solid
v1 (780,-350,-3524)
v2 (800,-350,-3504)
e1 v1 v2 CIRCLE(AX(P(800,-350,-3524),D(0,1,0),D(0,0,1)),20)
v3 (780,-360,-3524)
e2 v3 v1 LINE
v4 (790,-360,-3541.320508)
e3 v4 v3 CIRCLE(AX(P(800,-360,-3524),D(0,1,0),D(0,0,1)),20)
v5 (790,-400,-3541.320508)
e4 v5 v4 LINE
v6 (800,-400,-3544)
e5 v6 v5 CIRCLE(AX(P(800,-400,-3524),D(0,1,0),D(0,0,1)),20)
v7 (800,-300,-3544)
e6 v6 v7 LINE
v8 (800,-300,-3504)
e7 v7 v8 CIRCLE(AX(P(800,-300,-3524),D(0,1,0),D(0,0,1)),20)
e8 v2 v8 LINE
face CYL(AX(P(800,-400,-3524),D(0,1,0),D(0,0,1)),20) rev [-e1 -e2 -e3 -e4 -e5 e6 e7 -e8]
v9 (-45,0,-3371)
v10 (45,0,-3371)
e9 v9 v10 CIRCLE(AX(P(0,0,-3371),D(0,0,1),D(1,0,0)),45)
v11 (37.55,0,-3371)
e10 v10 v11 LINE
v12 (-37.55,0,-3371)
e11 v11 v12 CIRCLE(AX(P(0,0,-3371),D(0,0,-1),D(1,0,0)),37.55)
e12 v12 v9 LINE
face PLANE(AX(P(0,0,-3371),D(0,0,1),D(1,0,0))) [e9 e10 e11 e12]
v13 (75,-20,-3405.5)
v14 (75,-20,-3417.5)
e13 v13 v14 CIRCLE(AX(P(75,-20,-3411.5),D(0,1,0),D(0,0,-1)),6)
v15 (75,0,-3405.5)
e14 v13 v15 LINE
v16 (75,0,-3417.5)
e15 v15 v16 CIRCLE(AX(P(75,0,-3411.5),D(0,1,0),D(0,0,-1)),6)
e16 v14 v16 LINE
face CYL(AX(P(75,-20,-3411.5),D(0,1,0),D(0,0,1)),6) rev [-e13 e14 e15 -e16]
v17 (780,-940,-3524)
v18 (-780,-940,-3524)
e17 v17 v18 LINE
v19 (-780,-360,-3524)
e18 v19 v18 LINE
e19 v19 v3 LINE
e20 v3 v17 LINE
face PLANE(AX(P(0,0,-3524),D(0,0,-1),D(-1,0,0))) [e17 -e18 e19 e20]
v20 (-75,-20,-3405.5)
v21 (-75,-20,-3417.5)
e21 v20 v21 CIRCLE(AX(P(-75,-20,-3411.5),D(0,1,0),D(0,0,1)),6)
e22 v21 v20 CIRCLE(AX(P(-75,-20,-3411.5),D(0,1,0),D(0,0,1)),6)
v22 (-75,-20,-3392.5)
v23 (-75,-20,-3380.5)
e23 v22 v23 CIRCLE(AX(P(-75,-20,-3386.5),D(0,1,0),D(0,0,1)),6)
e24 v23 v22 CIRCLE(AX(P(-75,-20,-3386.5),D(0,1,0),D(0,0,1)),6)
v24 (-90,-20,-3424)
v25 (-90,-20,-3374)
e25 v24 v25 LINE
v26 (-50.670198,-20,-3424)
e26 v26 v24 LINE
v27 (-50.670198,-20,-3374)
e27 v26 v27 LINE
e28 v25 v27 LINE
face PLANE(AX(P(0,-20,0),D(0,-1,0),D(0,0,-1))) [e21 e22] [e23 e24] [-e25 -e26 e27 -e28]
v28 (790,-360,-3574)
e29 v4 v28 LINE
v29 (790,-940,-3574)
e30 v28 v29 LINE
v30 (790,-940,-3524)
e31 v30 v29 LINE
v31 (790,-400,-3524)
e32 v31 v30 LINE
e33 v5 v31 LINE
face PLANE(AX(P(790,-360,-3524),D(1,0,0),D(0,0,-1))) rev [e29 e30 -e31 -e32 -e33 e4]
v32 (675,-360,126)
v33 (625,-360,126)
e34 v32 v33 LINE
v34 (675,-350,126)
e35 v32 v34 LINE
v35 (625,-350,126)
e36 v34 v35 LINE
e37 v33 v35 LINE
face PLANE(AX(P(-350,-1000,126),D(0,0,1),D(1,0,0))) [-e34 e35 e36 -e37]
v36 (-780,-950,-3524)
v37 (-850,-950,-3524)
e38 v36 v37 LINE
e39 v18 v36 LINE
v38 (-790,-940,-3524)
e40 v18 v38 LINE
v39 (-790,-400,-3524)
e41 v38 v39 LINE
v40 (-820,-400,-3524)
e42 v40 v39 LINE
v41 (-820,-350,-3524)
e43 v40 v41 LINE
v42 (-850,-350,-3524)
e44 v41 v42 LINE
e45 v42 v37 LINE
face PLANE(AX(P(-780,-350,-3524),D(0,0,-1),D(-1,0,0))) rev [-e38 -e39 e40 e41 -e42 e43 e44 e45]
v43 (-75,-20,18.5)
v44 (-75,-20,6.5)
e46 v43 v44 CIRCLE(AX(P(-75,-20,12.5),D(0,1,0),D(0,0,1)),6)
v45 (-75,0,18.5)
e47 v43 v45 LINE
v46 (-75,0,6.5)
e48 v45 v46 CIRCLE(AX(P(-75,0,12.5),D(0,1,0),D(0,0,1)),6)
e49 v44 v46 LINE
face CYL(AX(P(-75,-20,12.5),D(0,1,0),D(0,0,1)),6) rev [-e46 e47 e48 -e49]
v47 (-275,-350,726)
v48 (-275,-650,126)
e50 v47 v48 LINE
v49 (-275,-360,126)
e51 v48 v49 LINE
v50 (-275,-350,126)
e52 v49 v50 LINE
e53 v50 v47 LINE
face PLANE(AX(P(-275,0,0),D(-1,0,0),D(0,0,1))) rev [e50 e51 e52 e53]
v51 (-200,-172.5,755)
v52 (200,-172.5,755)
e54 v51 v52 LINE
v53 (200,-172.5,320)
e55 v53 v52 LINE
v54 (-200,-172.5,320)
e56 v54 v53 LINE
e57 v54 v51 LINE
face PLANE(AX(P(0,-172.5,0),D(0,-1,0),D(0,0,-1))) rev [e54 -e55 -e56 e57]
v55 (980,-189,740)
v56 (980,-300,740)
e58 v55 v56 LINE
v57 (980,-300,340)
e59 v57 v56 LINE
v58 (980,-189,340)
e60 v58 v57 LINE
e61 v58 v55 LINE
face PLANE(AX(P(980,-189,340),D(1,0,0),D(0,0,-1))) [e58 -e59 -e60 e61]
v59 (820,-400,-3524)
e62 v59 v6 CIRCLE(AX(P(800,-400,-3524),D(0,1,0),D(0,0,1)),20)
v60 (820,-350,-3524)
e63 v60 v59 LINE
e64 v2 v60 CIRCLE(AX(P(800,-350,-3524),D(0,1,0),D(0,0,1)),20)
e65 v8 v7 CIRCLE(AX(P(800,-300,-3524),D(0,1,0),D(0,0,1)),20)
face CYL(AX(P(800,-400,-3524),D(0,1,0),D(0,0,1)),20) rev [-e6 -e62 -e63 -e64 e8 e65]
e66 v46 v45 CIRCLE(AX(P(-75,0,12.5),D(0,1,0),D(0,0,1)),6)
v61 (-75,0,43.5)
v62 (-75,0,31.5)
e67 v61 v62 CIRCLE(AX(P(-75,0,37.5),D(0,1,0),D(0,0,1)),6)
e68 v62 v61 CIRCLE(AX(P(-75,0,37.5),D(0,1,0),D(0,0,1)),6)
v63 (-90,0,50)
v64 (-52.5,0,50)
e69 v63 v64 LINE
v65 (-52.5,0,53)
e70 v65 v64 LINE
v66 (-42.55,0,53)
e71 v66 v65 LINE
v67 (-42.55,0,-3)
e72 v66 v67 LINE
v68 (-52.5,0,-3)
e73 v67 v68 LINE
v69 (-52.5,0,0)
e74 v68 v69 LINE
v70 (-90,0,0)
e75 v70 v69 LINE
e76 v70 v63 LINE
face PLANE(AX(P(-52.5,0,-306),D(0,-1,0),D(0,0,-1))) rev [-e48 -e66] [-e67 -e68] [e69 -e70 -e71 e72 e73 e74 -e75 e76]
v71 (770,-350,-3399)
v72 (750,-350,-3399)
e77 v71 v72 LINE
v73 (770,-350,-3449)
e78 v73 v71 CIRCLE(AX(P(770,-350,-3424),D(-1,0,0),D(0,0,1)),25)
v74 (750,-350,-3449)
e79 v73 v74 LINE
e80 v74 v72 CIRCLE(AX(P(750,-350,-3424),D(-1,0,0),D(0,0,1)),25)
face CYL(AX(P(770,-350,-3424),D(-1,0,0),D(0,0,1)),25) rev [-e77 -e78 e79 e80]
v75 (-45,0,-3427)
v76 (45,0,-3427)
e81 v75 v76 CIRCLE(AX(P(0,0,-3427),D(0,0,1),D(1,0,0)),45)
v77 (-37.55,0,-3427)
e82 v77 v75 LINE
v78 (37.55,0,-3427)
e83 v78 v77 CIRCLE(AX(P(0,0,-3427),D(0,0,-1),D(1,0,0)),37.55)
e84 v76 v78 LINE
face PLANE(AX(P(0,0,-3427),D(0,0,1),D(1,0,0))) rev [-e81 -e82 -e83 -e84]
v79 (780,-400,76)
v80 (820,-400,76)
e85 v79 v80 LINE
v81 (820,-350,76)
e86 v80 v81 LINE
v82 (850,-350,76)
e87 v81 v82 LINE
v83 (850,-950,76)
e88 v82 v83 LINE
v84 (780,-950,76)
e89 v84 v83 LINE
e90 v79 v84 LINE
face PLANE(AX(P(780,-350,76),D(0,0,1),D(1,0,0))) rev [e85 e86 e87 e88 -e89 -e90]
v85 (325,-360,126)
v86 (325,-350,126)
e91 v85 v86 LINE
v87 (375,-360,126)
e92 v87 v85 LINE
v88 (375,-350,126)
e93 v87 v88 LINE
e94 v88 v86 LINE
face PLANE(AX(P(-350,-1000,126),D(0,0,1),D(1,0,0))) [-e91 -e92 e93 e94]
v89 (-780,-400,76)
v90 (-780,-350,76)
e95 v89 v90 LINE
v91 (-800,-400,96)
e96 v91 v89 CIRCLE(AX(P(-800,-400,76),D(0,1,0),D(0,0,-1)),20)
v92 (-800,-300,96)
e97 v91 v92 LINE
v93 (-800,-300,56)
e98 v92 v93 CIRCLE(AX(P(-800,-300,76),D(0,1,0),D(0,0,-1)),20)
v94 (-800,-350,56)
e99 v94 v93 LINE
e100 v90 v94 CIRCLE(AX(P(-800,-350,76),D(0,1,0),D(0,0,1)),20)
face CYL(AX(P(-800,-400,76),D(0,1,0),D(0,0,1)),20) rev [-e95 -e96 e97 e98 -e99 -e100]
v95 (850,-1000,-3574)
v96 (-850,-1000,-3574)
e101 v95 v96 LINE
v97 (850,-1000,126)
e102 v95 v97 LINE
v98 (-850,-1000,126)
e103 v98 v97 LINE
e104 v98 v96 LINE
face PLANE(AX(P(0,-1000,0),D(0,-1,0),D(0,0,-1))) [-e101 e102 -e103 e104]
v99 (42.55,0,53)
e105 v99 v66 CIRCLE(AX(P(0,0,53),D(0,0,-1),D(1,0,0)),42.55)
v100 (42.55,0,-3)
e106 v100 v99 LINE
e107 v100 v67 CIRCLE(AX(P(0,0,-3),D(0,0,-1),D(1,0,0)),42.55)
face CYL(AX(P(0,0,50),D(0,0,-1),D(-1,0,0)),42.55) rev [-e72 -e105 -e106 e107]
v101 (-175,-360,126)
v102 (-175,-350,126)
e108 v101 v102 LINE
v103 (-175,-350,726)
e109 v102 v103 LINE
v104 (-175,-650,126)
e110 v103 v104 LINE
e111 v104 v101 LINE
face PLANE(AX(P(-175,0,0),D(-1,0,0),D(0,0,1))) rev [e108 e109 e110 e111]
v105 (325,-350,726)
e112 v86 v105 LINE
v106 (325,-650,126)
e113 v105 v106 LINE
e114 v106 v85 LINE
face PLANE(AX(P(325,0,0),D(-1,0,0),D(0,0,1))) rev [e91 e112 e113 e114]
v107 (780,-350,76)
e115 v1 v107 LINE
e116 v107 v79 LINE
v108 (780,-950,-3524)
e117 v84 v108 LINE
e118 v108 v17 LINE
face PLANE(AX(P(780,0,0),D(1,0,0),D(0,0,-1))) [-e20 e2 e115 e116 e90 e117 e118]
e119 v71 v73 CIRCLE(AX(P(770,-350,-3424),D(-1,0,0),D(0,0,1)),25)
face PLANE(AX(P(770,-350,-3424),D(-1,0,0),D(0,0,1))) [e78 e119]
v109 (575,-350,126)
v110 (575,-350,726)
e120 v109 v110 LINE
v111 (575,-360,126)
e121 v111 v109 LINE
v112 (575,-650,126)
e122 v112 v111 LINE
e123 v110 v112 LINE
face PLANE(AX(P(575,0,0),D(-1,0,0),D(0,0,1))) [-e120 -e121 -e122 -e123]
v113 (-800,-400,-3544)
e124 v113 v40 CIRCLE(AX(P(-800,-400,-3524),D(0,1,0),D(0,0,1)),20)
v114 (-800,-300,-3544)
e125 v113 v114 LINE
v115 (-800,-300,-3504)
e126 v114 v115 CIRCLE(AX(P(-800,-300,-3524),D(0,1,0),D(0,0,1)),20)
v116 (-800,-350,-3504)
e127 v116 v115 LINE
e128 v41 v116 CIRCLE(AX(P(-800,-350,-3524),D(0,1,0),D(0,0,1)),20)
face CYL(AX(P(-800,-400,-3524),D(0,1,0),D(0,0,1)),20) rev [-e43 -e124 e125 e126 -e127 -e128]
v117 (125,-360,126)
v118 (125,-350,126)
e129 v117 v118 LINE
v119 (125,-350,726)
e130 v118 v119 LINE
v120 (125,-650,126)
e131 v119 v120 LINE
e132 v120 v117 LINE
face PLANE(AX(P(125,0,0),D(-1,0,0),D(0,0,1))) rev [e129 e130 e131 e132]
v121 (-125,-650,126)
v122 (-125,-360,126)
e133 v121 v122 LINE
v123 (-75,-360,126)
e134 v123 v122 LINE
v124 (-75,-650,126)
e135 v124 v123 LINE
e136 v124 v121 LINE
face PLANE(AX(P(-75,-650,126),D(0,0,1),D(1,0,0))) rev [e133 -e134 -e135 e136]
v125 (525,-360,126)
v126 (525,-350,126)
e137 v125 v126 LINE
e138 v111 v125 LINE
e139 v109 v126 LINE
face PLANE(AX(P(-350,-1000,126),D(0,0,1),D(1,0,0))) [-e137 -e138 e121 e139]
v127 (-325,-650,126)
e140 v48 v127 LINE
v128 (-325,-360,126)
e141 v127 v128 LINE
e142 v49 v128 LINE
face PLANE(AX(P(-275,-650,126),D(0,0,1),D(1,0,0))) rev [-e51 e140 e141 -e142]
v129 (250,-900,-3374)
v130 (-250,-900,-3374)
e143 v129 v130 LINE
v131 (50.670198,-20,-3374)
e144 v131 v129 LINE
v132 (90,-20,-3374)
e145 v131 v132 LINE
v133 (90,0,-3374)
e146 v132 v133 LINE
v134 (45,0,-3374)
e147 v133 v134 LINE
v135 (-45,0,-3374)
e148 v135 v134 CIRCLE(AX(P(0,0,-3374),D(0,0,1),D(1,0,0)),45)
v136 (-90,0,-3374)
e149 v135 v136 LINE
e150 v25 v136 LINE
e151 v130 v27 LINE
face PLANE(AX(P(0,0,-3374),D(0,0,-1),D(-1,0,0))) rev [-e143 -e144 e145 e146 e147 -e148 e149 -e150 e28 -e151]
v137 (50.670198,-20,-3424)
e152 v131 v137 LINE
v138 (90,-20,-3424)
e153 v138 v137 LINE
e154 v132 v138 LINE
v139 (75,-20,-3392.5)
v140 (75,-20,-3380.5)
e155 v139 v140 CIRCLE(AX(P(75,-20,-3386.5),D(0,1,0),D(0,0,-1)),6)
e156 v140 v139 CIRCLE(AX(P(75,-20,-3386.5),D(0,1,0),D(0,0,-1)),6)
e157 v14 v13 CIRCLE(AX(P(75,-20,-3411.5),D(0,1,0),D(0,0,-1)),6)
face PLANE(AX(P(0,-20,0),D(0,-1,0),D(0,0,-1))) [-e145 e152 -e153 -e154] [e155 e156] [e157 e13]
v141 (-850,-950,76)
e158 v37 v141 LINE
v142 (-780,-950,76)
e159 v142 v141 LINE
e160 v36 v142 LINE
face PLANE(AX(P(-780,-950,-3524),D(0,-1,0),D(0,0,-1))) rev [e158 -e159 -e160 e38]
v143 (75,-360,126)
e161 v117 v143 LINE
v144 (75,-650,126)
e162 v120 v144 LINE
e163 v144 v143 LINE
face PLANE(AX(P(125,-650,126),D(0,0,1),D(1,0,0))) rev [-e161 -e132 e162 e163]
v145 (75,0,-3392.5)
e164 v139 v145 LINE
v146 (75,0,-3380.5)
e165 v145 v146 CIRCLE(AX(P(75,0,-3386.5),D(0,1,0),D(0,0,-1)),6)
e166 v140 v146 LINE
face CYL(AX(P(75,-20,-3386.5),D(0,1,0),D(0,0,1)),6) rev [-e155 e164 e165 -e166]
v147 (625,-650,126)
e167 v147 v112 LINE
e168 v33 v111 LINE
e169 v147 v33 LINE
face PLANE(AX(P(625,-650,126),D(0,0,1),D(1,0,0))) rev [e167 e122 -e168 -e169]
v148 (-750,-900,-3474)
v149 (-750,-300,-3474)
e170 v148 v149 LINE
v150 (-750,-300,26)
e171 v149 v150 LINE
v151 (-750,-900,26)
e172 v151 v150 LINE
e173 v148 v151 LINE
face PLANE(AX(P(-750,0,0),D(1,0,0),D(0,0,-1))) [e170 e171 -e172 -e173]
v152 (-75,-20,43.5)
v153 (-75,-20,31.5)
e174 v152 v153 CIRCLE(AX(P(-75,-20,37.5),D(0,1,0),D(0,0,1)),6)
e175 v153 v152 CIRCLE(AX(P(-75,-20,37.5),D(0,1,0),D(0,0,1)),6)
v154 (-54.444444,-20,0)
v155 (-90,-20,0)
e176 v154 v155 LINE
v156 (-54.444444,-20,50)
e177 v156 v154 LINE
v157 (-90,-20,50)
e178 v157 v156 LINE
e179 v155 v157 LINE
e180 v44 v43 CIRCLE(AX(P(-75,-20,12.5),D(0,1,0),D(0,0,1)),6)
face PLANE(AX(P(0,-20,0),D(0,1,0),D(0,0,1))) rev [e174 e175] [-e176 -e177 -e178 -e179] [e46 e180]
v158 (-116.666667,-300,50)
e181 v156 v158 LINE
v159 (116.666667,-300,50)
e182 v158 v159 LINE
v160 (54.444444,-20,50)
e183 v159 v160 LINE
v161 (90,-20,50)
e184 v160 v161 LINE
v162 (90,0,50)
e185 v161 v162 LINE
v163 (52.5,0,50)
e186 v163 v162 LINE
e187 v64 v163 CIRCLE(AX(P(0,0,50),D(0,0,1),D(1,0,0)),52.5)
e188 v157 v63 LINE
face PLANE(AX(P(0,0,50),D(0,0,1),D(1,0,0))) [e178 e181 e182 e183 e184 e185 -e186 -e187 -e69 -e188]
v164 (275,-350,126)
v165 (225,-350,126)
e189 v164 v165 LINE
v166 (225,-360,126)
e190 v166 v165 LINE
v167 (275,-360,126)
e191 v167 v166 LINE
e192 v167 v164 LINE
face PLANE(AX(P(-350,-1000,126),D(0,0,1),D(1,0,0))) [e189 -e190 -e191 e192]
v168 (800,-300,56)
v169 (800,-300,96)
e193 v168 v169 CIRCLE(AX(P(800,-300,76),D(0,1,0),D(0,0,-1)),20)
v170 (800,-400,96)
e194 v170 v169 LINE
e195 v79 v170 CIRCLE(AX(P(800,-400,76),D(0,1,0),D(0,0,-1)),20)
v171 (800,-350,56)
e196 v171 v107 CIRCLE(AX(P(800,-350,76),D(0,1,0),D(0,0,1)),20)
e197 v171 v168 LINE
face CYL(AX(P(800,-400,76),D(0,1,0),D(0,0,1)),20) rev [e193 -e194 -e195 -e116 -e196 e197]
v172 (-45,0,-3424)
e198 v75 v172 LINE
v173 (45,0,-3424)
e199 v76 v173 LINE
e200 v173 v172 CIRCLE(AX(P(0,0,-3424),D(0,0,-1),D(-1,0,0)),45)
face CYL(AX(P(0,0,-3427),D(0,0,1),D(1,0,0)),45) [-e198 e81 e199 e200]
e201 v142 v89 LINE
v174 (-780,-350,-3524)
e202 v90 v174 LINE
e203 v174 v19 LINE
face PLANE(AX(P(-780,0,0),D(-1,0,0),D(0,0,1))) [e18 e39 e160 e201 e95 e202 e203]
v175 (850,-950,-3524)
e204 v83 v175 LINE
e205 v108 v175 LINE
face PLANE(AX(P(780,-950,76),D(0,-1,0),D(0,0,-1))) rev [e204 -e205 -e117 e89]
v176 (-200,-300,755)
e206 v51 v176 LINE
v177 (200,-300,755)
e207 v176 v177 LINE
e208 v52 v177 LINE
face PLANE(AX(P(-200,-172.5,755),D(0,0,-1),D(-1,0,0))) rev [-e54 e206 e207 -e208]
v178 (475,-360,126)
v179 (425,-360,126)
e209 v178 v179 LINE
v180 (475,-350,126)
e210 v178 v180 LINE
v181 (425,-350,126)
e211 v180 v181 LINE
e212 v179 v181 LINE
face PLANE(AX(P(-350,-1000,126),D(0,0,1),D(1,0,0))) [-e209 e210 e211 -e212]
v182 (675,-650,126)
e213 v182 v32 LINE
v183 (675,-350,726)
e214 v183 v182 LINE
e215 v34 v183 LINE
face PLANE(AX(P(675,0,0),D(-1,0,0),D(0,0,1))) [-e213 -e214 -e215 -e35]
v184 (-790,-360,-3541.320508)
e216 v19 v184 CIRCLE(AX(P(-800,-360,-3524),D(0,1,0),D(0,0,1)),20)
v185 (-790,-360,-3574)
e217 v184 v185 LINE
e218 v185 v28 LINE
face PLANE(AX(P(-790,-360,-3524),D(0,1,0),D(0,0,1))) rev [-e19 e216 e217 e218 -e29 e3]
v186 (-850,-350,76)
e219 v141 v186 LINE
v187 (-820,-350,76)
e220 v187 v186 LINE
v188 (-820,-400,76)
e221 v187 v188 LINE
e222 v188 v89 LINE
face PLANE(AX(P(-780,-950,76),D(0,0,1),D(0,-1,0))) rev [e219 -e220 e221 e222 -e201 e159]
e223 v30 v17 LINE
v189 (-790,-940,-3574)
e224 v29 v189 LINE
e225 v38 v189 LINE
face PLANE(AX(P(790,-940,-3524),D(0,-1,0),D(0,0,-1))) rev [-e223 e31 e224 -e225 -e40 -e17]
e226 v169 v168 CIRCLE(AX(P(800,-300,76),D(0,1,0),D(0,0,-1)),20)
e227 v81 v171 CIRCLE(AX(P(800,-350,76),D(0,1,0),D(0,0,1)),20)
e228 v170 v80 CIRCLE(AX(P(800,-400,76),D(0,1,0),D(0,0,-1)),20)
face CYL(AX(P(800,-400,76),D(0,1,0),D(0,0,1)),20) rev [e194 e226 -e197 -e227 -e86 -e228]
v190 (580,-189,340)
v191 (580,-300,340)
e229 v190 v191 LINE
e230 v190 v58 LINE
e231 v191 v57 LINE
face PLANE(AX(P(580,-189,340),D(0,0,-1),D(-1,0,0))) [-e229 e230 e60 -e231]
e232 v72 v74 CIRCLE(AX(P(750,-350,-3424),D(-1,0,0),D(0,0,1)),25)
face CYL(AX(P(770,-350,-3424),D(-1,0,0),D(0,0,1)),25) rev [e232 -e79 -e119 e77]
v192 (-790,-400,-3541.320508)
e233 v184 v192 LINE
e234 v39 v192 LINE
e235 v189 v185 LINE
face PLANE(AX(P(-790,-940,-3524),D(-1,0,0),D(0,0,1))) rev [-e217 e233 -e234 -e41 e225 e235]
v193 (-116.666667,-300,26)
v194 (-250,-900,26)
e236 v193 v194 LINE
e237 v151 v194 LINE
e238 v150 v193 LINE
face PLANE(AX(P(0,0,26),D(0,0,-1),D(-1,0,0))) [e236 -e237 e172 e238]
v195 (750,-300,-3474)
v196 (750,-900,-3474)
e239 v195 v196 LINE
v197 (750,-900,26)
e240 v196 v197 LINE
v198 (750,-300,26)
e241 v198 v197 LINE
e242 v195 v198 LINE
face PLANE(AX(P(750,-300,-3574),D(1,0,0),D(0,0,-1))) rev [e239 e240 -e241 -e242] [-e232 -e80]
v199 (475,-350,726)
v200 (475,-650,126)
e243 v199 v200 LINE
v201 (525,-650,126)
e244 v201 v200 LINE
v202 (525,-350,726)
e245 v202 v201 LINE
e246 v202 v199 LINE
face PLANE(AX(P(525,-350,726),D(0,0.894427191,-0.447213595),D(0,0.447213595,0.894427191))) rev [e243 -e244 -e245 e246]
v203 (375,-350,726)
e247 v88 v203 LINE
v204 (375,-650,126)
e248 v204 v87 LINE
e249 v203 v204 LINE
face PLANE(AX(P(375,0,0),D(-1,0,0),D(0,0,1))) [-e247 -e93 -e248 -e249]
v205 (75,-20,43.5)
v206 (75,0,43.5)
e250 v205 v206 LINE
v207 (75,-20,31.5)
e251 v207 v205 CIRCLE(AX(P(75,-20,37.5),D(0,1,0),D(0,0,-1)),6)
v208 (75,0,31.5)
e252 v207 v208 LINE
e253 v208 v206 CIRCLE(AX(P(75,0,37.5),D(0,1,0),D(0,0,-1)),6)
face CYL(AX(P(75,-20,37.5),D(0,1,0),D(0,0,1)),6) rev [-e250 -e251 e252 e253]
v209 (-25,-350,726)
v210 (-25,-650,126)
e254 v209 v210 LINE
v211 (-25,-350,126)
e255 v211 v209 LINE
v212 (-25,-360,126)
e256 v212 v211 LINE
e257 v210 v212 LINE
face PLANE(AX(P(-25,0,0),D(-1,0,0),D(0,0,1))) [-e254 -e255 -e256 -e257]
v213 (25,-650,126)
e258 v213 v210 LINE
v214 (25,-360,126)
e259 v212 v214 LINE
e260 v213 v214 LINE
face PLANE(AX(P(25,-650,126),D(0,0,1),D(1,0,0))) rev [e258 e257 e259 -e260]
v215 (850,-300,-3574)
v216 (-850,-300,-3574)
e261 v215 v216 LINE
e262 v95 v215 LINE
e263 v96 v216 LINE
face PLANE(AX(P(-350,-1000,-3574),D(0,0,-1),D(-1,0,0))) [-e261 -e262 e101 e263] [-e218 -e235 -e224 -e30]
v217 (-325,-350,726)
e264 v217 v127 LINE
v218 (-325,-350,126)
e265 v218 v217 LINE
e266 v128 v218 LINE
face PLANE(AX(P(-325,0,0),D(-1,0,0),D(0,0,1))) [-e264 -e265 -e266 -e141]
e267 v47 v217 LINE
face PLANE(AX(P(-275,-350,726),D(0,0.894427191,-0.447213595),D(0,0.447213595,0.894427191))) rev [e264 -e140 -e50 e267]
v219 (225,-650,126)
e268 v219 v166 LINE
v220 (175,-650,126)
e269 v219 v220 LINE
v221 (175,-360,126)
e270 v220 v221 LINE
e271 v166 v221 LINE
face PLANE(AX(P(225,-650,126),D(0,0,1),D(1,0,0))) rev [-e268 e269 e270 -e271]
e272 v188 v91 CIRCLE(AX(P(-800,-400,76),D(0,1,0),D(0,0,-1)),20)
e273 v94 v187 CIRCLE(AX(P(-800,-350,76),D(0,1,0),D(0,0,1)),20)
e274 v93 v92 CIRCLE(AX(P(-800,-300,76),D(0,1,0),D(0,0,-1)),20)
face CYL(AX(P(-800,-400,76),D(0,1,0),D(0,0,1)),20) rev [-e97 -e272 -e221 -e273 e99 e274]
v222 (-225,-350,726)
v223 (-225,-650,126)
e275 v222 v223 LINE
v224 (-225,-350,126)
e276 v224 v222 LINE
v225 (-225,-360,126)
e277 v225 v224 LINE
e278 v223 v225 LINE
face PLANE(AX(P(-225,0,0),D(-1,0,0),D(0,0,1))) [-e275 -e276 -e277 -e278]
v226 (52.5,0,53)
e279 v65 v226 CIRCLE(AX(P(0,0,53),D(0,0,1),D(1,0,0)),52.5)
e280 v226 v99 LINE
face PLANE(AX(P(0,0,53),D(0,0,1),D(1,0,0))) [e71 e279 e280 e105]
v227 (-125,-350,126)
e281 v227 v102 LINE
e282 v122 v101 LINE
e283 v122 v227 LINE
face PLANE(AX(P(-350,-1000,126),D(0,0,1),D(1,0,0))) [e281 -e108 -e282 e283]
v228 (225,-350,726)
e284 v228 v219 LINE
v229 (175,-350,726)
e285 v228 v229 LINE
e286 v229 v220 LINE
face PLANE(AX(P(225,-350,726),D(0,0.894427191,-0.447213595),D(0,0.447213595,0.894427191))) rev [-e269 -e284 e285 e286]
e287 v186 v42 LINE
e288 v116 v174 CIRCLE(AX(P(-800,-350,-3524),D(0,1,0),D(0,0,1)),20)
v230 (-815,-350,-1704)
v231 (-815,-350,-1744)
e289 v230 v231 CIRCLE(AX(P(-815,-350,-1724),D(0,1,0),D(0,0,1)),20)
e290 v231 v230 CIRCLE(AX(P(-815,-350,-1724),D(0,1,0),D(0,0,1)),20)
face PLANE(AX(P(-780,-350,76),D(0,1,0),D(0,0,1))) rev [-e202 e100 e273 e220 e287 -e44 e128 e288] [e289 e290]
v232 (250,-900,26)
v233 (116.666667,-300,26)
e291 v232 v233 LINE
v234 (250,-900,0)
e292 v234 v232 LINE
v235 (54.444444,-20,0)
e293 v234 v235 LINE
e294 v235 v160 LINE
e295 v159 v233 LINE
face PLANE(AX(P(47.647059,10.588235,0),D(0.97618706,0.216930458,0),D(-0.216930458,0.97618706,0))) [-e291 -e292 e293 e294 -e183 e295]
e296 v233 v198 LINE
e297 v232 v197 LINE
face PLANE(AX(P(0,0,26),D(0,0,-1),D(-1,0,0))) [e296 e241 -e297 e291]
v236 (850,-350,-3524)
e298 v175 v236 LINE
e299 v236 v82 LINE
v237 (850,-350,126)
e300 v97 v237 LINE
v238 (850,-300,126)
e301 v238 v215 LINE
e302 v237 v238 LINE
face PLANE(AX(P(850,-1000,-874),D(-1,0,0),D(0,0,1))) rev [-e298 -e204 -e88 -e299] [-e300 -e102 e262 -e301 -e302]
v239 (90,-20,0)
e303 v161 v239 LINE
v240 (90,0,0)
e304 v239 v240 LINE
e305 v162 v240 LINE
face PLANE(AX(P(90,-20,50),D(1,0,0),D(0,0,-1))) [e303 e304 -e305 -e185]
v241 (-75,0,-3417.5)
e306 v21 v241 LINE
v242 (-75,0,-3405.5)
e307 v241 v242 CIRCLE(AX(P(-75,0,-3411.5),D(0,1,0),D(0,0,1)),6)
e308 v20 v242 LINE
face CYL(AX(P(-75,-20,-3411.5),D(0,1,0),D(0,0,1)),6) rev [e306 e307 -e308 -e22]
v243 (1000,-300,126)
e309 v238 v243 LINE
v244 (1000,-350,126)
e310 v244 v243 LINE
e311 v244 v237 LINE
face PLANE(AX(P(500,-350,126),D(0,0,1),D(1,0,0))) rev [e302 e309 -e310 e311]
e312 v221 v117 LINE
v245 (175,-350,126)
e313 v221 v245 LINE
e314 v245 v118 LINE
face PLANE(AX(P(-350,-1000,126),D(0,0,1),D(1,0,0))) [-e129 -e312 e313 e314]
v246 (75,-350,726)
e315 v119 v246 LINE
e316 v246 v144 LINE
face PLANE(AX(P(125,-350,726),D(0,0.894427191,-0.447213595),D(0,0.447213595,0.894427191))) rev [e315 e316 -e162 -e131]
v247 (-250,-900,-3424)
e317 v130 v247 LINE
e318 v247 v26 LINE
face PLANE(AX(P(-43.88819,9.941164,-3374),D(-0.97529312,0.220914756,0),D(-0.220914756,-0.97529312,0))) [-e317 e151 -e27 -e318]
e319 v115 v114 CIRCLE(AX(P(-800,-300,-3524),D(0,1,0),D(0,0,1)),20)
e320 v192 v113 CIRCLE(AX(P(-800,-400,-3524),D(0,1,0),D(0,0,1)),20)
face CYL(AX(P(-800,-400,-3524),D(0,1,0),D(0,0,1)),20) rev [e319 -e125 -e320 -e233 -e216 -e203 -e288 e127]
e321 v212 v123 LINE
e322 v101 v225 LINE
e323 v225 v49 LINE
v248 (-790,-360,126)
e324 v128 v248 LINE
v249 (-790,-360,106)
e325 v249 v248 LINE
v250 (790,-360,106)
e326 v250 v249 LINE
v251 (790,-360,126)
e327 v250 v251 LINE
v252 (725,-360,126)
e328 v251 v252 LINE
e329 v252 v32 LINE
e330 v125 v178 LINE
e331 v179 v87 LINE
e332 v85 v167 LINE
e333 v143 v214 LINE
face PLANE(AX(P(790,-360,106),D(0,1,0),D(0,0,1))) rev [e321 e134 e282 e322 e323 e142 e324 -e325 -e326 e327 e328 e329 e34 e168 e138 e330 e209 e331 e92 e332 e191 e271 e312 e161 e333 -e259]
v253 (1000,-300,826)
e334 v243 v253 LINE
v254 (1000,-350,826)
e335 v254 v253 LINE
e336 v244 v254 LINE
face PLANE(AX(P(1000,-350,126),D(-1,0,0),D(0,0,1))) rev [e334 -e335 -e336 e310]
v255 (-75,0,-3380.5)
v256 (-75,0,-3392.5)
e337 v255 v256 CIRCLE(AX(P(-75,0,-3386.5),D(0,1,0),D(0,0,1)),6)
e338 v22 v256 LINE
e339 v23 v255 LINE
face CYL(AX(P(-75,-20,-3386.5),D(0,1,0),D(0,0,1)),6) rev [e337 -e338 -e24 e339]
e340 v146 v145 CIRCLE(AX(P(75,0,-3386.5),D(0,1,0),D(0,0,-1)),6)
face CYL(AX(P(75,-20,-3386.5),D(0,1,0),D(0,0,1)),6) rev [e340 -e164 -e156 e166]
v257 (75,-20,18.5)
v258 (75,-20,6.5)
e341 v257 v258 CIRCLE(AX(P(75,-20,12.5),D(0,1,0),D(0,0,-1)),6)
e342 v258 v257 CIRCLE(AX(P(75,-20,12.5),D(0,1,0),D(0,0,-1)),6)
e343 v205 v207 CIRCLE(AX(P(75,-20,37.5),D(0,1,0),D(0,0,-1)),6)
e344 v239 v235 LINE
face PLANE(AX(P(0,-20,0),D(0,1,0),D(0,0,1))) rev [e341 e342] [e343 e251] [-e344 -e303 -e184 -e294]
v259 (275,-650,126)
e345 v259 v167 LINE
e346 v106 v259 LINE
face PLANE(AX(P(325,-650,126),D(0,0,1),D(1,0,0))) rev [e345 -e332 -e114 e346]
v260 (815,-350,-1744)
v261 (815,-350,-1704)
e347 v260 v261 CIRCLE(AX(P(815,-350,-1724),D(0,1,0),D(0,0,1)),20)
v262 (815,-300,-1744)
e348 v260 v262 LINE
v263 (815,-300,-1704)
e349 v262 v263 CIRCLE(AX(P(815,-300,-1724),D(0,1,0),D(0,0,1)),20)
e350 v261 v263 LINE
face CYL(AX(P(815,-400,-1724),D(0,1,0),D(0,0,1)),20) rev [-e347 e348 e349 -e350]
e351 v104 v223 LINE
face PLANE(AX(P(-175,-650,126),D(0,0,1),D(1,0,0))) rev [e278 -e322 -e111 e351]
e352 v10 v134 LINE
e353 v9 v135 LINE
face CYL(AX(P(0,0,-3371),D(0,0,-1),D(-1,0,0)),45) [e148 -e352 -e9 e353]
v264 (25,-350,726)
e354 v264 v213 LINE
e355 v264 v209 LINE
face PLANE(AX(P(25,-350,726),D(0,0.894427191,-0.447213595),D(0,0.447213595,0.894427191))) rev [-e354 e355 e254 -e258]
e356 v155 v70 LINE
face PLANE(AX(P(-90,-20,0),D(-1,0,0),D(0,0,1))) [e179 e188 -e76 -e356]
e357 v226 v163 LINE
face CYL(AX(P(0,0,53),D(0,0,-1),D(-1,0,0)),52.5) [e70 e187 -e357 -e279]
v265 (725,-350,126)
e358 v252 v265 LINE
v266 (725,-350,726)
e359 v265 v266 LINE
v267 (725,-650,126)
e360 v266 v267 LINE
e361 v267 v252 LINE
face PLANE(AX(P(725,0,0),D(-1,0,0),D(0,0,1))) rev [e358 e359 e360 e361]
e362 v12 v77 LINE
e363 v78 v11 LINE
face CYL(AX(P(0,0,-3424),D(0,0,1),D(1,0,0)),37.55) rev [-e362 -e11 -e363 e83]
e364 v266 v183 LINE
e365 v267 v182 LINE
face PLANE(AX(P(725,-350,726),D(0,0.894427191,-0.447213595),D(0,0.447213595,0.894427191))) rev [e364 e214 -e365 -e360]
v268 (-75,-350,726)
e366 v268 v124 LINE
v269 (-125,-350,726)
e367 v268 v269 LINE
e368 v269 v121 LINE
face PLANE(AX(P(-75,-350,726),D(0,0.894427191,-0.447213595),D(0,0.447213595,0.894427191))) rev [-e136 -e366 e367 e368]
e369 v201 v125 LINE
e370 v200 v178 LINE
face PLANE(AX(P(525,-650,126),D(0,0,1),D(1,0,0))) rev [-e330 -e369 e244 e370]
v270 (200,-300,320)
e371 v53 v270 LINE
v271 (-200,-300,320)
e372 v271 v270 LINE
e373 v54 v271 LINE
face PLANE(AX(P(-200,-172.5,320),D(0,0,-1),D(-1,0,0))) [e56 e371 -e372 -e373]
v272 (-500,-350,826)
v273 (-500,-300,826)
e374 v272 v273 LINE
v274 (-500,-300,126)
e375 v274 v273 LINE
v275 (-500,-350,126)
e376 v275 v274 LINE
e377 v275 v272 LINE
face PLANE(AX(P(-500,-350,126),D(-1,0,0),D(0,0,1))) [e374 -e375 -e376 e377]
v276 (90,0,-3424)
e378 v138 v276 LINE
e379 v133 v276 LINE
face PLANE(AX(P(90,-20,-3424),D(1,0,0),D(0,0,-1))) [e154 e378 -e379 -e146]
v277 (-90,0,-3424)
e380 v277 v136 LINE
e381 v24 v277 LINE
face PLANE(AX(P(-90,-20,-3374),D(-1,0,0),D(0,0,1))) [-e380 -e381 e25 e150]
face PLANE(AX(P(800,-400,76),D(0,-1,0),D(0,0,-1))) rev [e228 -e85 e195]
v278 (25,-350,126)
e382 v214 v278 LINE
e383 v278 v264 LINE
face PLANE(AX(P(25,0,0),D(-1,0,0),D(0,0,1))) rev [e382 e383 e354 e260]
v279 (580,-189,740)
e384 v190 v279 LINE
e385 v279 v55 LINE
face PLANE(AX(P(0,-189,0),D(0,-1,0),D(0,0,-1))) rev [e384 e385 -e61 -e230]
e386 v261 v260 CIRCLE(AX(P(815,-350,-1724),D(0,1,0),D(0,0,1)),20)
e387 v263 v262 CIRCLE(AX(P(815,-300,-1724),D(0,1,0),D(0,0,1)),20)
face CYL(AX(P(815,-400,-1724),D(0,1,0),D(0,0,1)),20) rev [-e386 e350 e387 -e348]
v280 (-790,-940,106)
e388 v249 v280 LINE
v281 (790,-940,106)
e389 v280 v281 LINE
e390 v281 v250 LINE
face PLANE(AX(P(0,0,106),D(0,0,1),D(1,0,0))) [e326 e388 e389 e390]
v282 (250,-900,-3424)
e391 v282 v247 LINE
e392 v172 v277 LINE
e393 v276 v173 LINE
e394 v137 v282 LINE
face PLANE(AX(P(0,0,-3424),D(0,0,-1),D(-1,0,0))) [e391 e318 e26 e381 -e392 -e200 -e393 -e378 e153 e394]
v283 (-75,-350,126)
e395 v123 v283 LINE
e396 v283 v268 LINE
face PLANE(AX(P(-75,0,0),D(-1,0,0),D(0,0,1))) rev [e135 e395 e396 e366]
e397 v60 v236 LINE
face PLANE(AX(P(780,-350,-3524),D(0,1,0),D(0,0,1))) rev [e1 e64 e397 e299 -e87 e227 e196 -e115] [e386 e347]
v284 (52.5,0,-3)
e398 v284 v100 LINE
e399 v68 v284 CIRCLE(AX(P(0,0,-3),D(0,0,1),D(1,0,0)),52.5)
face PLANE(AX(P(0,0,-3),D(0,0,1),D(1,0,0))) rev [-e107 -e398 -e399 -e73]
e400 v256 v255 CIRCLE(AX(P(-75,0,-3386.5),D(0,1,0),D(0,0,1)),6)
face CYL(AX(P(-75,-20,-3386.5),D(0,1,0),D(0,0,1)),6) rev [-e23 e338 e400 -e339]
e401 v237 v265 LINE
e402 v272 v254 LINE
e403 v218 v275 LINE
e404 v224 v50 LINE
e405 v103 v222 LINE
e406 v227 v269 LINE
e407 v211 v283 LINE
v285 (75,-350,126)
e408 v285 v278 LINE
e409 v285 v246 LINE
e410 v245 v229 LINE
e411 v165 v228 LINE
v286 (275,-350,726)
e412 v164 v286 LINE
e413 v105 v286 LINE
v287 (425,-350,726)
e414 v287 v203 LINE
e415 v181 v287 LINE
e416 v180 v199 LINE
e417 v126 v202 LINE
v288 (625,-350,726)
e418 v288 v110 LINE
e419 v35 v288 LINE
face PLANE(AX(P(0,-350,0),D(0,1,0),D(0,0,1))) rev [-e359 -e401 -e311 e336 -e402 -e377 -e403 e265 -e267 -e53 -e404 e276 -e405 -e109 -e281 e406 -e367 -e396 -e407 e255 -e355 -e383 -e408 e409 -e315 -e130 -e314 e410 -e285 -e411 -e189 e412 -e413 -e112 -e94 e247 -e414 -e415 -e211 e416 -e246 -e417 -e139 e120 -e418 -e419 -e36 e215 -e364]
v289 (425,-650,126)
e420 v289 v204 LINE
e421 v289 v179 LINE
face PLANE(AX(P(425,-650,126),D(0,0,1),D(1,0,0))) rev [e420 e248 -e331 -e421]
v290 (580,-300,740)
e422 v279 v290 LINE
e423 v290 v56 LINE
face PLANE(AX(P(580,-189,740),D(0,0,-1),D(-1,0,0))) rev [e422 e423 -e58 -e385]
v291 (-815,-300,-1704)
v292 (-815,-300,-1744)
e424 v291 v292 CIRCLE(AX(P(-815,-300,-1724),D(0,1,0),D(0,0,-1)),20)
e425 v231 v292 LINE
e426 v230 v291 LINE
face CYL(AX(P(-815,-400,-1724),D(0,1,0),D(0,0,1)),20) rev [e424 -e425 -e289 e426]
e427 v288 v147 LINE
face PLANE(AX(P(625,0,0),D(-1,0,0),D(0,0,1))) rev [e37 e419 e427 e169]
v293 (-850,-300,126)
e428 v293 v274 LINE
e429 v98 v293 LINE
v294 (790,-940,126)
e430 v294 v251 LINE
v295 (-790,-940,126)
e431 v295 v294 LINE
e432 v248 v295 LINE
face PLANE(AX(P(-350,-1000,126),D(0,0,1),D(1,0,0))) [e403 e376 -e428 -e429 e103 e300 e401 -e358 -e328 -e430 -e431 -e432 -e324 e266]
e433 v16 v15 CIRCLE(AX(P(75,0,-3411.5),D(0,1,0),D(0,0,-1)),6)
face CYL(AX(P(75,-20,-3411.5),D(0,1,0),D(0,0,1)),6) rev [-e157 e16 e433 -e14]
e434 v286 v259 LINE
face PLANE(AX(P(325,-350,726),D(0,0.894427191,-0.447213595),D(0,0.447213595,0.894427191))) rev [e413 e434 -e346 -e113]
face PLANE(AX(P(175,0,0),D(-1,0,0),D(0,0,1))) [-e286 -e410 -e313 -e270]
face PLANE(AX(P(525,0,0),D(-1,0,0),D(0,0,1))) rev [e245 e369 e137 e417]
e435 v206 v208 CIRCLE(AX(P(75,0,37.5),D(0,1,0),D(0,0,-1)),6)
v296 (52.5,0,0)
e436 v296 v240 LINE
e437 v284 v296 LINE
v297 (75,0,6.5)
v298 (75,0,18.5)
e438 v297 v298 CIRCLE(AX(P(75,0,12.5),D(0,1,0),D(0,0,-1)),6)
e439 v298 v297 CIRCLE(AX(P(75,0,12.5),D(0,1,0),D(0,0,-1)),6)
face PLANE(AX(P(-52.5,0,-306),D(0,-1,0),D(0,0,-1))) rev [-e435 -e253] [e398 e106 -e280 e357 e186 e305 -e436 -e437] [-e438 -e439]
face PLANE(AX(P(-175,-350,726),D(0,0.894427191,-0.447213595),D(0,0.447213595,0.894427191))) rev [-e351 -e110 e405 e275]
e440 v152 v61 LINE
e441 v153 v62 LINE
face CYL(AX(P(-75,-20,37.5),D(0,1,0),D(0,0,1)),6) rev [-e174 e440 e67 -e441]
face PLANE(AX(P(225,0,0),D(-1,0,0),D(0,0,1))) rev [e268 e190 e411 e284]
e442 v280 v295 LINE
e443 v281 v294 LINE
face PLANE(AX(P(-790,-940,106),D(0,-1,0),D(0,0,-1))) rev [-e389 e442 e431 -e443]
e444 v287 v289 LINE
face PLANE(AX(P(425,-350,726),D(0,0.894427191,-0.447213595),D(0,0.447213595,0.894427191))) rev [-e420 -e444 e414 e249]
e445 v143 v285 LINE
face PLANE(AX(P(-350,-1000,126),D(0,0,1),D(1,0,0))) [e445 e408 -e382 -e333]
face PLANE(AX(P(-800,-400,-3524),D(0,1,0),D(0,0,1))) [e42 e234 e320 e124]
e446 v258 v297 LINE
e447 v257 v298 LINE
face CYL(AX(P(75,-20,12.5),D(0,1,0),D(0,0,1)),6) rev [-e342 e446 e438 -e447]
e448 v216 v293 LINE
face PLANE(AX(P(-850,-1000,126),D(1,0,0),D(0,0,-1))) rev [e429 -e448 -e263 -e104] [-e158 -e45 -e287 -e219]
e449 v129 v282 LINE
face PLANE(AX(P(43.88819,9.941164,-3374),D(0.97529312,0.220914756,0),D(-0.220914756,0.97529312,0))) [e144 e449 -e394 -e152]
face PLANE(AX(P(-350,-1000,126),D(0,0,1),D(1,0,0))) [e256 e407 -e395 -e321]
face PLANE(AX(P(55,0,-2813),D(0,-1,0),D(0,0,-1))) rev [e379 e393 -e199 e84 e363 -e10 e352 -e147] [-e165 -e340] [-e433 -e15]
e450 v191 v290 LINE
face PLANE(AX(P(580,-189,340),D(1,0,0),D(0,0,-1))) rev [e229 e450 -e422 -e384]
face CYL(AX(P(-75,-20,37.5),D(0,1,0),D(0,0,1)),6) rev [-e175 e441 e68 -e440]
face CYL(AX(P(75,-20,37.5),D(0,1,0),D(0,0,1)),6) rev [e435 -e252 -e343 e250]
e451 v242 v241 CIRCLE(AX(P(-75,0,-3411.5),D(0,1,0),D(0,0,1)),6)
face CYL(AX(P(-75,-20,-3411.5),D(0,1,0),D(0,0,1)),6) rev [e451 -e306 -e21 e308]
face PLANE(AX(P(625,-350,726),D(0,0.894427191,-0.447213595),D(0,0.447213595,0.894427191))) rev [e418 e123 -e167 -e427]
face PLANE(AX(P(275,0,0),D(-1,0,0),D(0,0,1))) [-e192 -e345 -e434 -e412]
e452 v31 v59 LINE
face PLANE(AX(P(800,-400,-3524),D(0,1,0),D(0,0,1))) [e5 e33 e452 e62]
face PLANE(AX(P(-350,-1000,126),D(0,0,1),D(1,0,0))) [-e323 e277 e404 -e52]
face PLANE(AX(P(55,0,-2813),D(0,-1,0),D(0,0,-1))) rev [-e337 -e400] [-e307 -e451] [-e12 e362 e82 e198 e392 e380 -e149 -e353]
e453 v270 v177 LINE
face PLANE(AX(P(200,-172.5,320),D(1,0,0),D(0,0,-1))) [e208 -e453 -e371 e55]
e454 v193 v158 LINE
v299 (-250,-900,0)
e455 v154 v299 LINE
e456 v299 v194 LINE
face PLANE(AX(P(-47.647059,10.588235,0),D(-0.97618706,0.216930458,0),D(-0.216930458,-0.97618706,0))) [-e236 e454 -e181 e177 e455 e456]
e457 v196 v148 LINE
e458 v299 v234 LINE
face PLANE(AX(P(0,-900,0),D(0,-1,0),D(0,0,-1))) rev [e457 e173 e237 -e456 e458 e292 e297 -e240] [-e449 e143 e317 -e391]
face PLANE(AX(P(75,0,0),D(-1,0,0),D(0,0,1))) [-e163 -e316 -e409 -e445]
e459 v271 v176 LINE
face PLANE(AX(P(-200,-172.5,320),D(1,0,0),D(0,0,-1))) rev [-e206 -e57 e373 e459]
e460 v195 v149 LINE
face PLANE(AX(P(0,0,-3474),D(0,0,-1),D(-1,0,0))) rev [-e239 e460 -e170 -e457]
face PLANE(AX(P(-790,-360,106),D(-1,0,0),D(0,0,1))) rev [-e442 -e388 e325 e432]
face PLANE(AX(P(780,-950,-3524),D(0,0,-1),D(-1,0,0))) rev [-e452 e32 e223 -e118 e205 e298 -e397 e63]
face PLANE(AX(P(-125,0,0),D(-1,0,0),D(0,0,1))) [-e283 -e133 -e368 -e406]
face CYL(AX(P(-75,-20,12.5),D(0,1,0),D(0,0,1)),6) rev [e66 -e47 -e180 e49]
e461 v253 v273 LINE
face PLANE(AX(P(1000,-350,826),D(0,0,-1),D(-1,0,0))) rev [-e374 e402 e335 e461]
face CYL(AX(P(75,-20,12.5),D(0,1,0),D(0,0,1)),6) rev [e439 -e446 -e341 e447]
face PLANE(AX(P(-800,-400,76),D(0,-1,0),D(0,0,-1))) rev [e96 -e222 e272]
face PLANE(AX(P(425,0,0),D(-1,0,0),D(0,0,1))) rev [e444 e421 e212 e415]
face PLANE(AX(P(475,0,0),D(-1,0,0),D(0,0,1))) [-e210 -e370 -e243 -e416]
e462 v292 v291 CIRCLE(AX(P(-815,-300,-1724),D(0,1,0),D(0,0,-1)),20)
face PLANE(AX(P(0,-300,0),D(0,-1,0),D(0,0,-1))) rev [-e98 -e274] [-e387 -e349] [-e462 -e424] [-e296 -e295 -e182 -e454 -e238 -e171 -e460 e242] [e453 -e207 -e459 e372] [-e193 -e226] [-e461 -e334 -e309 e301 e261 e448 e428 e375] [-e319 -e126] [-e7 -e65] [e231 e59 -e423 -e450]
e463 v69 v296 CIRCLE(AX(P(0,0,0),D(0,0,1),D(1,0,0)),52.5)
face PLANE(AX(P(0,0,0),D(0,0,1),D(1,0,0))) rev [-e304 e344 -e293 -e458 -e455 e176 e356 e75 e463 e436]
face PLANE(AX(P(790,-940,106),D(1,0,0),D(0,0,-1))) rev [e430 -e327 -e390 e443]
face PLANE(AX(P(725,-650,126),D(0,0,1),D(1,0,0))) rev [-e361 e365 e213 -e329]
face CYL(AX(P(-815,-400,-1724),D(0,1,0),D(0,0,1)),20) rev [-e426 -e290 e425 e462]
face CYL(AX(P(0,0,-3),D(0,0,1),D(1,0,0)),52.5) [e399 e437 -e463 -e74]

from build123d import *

# Parameters (mm, degrees)
SKETCH_1_R             = 50
SKETCH_1_R_2           = 42.55
EXTRUDE_1_DEPTH        = 50
SKETCH_3_R             = 45
SKETCH_3_R_2           = 37.55
EXTRUDE_2_DEPTH        = 50
EXTRUDE_START          = -50
EXTRUDE_3_DEPTH        = 50
SKETCH_8_R             = 37.55
EXTRUDE_4_DEPTH        = 50
SKETCH_4_W             = 700
SKETCH_4_H             = 3700
EXTRUDE_5_DEPTH        = 100
SKETCH_12_W            = 500
SKETCH_12_H            = 1000
EXTRUDE_6_DEPTH        = 100
SKETCH_16_W            = 500
SKETCH_16_H            = 2700
EXTRUDE_8_DEPTH        = 100
SKETCH_17_W            = 100
SKETCH_17_H            = 100
EXTRUDE_9_DEPTH        = 600
SKETCH_18_W            = 100
SKETCH_18_H            = 100
EXTRUDE_10_DEPTH       = 600
SKETCH_19_W            = 100
SKETCH_19_H            = 100
EXTRUDE_11_DEPTH       = 3500
SKETCH_20_R            = 25
CUT_EXTRUDE_5_DEPTH    = 20
SKETCH_21_R            = 52.5
SKETCH_21_R_2          = 42.55
EXTRUDE_12_DEPTH       = 50
CUT_EXTRUDE_START      = -356
CUT_EXTRUDE_6_DEPTH    = 356
SKETCH_23_W            = 47.45
SKETCH_23_H            = 50
EXTRUDE_13_DEPTH       = 20
CUT_EXTRUDE_8_DEPTH    = 611
SKETCH_26_W            = 52.45
SKETCH_26_H            = 50
EXTRUDE_14_DEPTH       = 20
SKETCH_27_R            = 6
CUT_EXTRUDE_9_DEPTH    = 20
SKETCH_28_R            = 6
CUT_EXTRUDE_10_DEPTH   = 20
EXTRUDE_START_2        = -53
EXTRUDE_15_DEPTH       = 53
EXTRUDE_START_3        = 3
EXTRUDE_16_DEPTH       = 3
EXTRUDE_17_DEPTH       = 3
EXTRUDE_18_DEPTH       = 53
SKETCH_31_W            = 3500
SKETCH_31_H            = 500
EXTRUDE_19_DEPTH       = 100
SKETCH_33_W            = 500
SKETCH_33_H            = 3700
EXTRUDE_20_DEPTH       = 100
EXTRUDE_21_DEPTH       = 100
SKETCH_35_W            = 1500
SKETCH_35_H            = 600
EXTRUDE_22_DEPTH       = 100
SKETCH_36_W            = 1500
SKETCH_36_H            = 600
EXTRUDE_23_DEPTH       = 100
SKETCH_37_W            = 3600
SKETCH_37_H            = 600
CUT_EXTRUDE_11_DEPTH   = 70
SKETCH_38_W            = 1580
SKETCH_38_H            = 580
CUT_EXTRUDE_15_DEPTH   = 50
SKETCH_39_W            = 3600
SKETCH_39_H            = 600
CUT_EXTRUDE_16_DEPTH   = 70
SKETCH_40_W            = 1580
SKETCH_40_H            = 580
CUT_EXTRUDE_17_DEPTH   = 20
SKETCH_43_R            = 20
CUT_EXTRUDE_20_DEPTH   = 100
EXTRUDE_24_DEPTH       = 50
EXTRUDE_25_DEPTH       = 25
PATTERN_LINEAR_1_COUNT = 4
PATTERN_LINEAR_1_PITCH = 100
PATTERN_LINEAR_2_COUNT = 8
PATTERN_LINEAR_2_PITCH = 100
SKETCH_46_W            = 400
SKETCH_46_H            = 435
EXTRUDE_26_DEPTH       = 127.5
SKETCH_47_W            = 400
SKETCH_47_H            = 400
EXTRUDE_28_DEPTH       = 111


with BuildPart() as part:
    # 草图1 → 凸台-拉伸1 (new body)
    with BuildSketch(Plane.XY):
        Circle(SKETCH_1_R)
        Circle(SKETCH_1_R_2, mode=Mode.SUBTRACT)
    extrude(amount=EXTRUDE_1_DEPTH)

    # 草图7 → 凸台-拉伸3 (add)
    with BuildSketch(Plane.XY.offset(50).offset(EXTRUDE_START)):
        with BuildLine():
            ThreePointArc((50, 0), (0, -50), (-50, 0))
            Line((-50, 0), (-250, -900))
            Line((-250, -900), (250, -900))
            Line((250, -900), (50, 0))
        make_face()
    extrude(amount=EXTRUDE_3_DEPTH)



with BuildPart() as body_2:
    # 草图3 → 凸台-拉伸2 (new body)
    with BuildSketch(Plane(origin=(0, 0, -3374), x_dir=(-1, 0, 0), z_dir=(0, 0, -1))):
        Circle(SKETCH_3_R)
        Circle(SKETCH_3_R_2, mode=Mode.SUBTRACT)
    extrude(amount=EXTRUDE_2_DEPTH)

    # 草图8 → 凸台-拉伸4 (add)
    with BuildSketch(Plane(origin=(0, 0, -3424), x_dir=(-1, 0, 0), z_dir=(0, 0, -1))):
        with BuildLine():
            Line((-43.888190419, 9.941164005), (-250, -900))
            Line((-250, -900), (250, -900))
            Line((250, -900), (43.888190419, 9.941164005))
            ThreePointArc((43.888190419, 9.941164005), (0, 45), (-43.888190419, 9.941164005))
        make_face()
        Circle(SKETCH_8_R, mode=Mode.SUBTRACT)
    extrude(amount=-EXTRUDE_4_DEPTH)


with BuildPart() as part_1:
    add(part.part)

    add(body_2.part)  # 凸台-拉伸5 merges body 2
    # 草图4 → 凸台-拉伸5 (add)
    with BuildSketch(Plane(origin=(0, -900, 0), x_dir=(1, 0, 0), z_dir=(0, 1, 0))):
        with Locations((0, 1724)):
            Rectangle(SKETCH_4_W, SKETCH_4_H)
    extrude(amount=-EXTRUDE_5_DEPTH)

    # 草图12 → 凸台-拉伸6 (add)
    with BuildSketch(Plane(origin=(0, -900, 0), x_dir=(1, 0, 0), z_dir=(0, 1, 0))):
        with Locations((600, 374)):
            Rectangle(SKETCH_12_W, SKETCH_12_H)
    extrude(amount=-EXTRUDE_6_DEPTH)

    # 草图16 → 凸台-拉伸8 (add)
    with BuildSketch(Plane(origin=(0, -900, 0), x_dir=(1, 0, 0), z_dir=(0, 1, 0))):
        with Locations((600, 2224)):
            Rectangle(SKETCH_16_W, SKETCH_16_H)
    extrude(amount=-EXTRUDE_8_DEPTH)

    # 草图17 → 凸台-拉伸9 (add)
    with BuildSketch(Plane(origin=(0, -900, 0), x_dir=(1, 0, 0), z_dir=(0, 1, 0))):
        with Locations((800, 3524)):
            Rectangle(SKETCH_17_W, SKETCH_17_H)
    extrude(amount=EXTRUDE_9_DEPTH)

    # 草图18 → 凸台-拉伸10 (add)
    with BuildSketch(Plane(origin=(0, -900, 0), x_dir=(1, 0, 0), z_dir=(0, 1, 0))):
        with Locations((800, -76)):
            Rectangle(SKETCH_18_W, SKETCH_18_H)
    extrude(amount=EXTRUDE_10_DEPTH)

    # 草图19 → 凸台-拉伸11 (add)
    with BuildSketch(Plane.XY.offset(-3474)):
        with Locations((800, -350)):
            Rectangle(SKETCH_19_W, SKETCH_19_H)
    extrude(amount=EXTRUDE_11_DEPTH)

    # 草图20 → 切除-拉伸5 (cut)
    with BuildSketch(Plane.ZY.offset(-750)):
        with Locations((-3424, -350)):
            Circle(SKETCH_20_R)
    extrude(amount=-CUT_EXTRUDE_5_DEPTH, mode=Mode.SUBTRACT)

    # 草图21 → 凸台-拉伸12 (add)
    with BuildSketch(Plane.XY.offset(50).offset(EXTRUDE_START)):
        Circle(SKETCH_21_R)
        Circle(SKETCH_21_R_2, mode=Mode.SUBTRACT)
    extrude(amount=EXTRUDE_12_DEPTH)

    # 草图22 → 切除-拉伸6 (cut)
    with BuildSketch(Plane.XY.offset(50).offset(CUT_EXTRUDE_START)):
        with BuildLine():
            Line((-52.5, 0), (52.5, 0))
            ThreePointArc((52.5, 0), (0, 52.5), (-52.5, 0))
        make_face()
    extrude(amount=CUT_EXTRUDE_6_DEPTH, mode=Mode.SUBTRACT)

    # 草图23 → 凸台-拉伸13 (add)
    with BuildSketch(Plane(origin=(0, 0, 0), x_dir=(1, 0, 0), z_dir=(0, 1, 0))):
        with Locations((-66.275, -25)):
            Rectangle(SKETCH_23_W, SKETCH_23_H)
        with Locations((66.275, -25)):
            Rectangle(SKETCH_23_W, SKETCH_23_H)
    extrude(amount=-EXTRUDE_13_DEPTH)

    # 草图24 → 切除-拉伸8 (cut)
    with BuildSketch(Plane(origin=(0, 0, -3424), x_dir=(-1, 0, 0), z_dir=(0, 0, -1))):
        with BuildLine():
            Line((-55, 0), (55, 0))
            ThreePointArc((55, 0), (0, 55), (-55, 0))
        make_face()
    extrude(amount=-CUT_EXTRUDE_8_DEPTH, mode=Mode.SUBTRACT)

    # 草图26 → 凸台-拉伸14 (add)
    with BuildSketch(Plane(origin=(0, 0, 0), x_dir=(1, 0, 0), z_dir=(0, 1, 0))):
        with Locations((-63.775, 3399)):
            Rectangle(SKETCH_26_W, SKETCH_26_H)
        with Locations((63.775, 3399)):
            Rectangle(SKETCH_26_W, SKETCH_26_H)
    extrude(amount=-EXTRUDE_14_DEPTH)

    # 草图27 → 切除-拉伸9 (cut)
    with BuildSketch(Plane(origin=(0, 0, 0), x_dir=(1, 0, 0), z_dir=(0, 1, 0))):
        with Locations(Location((-75, -12.5, 0), (0, 0, 270))):
            Circle(SKETCH_27_R)
        with Locations(Location((-75, -37.5, 0), (0, 0, 270))):
            Circle(SKETCH_27_R)
        with Locations(Location((75, -37.5, 0), (0, 0, 90))):
            Circle(SKETCH_27_R)
        with Locations(Location((75, -12.5, 0), (0, 0, 90))):
            Circle(SKETCH_27_R)
    extrude(amount=-CUT_EXTRUDE_9_DEPTH, mode=Mode.SUBTRACT)

    # 草图28 → 切除-拉伸10 (cut)
    with BuildSketch(Plane(origin=(0, 0, 0), x_dir=(1, 0, 0), z_dir=(0, 1, 0))):
        with Locations(Location((-75, 3411.5, 0), (0, 0, 270))):
            Circle(SKETCH_28_R)
        with Locations(Location((-75, 3386.5, 0), (0, 0, 270))):
            Circle(SKETCH_28_R)
        with Locations(Location((75, 3386.5, 0), (0, 0, 90))):
            Circle(SKETCH_28_R)
        with Locations(Location((75, 3411.5, 0), (0, 0, 90))):
            Circle(SKETCH_28_R)
    extrude(amount=-CUT_EXTRUDE_10_DEPTH, mode=Mode.SUBTRACT)

    # 草图29 → 凸台-拉伸15 (add)
    with BuildSketch(Plane.XY.offset(50).offset(EXTRUDE_START_2)):
        with BuildLine():
            Line((-52.5, 0), (-42.55, 0))
            ThreePointArc((-42.55, 0), (0, -42.55), (42.55, 0))
            Line((42.55, 0), (52.5, 0))
            ThreePointArc((52.5, 0), (0, -52.5), (-52.5, 0))
        make_face()
    extrude(amount=EXTRUDE_15_DEPTH)

    # 草图30 → 凸台-拉伸16 (add)
    with BuildSketch(Plane.XY.offset(-3374).offset(EXTRUDE_START_3)):
        with BuildLine():
            Line((-45, 0), (-37.55, 0))
            ThreePointArc((-37.55, 0), (0, -37.55), (37.55, 0))
            Line((37.55, 0), (45, 0))
            ThreePointArc((45, 0), (0, -45), (-45, 0))
        make_face()
    extrude(amount=-EXTRUDE_16_DEPTH)

    # 草图29<2> → 凸台-拉伸17 (add)
    with BuildSketch(Plane.XY.offset(50)):
        with BuildLine():
            Line((-52.5, 0), (-42.55, 0))
            ThreePointArc((-42.55, 0), (0, -42.55), (42.55, 0))
            Line((42.55, 0), (52.5, 0))
            ThreePointArc((52.5, 0), (0, -52.5), (-52.5, 0))
        make_face()
    extrude(amount=EXTRUDE_17_DEPTH)

    # 草图30<2> → 凸台-拉伸18 (add)
    with BuildSketch(Plane.XY.offset(-3374)):
        with BuildLine():
            Line((-45, 0), (-37.55, 0))
            ThreePointArc((-37.55, 0), (0, -37.55), (37.55, 0))
            Line((37.55, 0), (45, 0))
            ThreePointArc((45, 0), (0, -45), (-45, 0))
        make_face()
    extrude(amount=-EXTRUDE_18_DEPTH)

    # 草图31 → 凸台-拉伸19 (add)
    with BuildSketch(Plane.ZY.offset(-750)):
        with Locations((-1724, -650)):
            Rectangle(SKETCH_31_W, SKETCH_31_H)
    extrude(amount=-EXTRUDE_19_DEPTH)

    # 草图33 → 凸台-拉伸20 (add)
    with BuildSketch(Plane(origin=(0, -900, 0), x_dir=(1, 0, 0), z_dir=(0, 1, 0))):
        with Locations((-600, 1724)):
            Rectangle(SKETCH_33_W, SKETCH_33_H)
    extrude(amount=-EXTRUDE_20_DEPTH)

    # 草图34 → 凸台-拉伸21 (add)
    with BuildSketch(Plane.ZY.offset(850)):
        Polygon((126, -300), (126, -900), (126, -1000), (-3574, -1000), (-3574, -900), (-3574, -300), align=None)
    extrude(amount=-EXTRUDE_21_DEPTH)

    # 草图35 → 凸台-拉伸22 (add)
    with BuildSketch(Plane(origin=(0, 0, -3574), x_dir=(-1, 0, 0), z_dir=(0, 0, -1))):
        with Locations((0, -600)):
            Rectangle(SKETCH_35_W, SKETCH_35_H)
    extrude(amount=-EXTRUDE_22_DEPTH)

    # 草图36 → 凸台-拉伸23 (add)
    with BuildSketch(Plane.XY.offset(126)):
        with Locations((0, -600)):
            Rectangle(SKETCH_36_W, SKETCH_36_H)
    extrude(amount=-EXTRUDE_23_DEPTH)

    # 草图37 → 切除-拉伸11 (cut)
    with BuildSketch(Plane.ZY.offset(850)):
        with Locations((-1724, -650)):
            Rectangle(SKETCH_37_W, SKETCH_37_H)
    extrude(amount=-CUT_EXTRUDE_11_DEPTH, mode=Mode.SUBTRACT)

    # 草图38 → 切除-拉伸15 (cut)
    with BuildSketch(Plane(origin=(0, 0, -3574), x_dir=(-1, 0, 0), z_dir=(0, 0, -1))):
        with Locations((0, -650)):
            Rectangle(SKETCH_38_W, SKETCH_38_H)
    extrude(amount=-CUT_EXTRUDE_15_DEPTH, mode=Mode.SUBTRACT)

    # 草图39 → 切除-拉伸16 (cut)
    with BuildSketch(Plane(origin=(850, 0, 0), x_dir=(0, 0, -1), z_dir=(1, 0, 0))):
        with Locations((1724, -650)):
            Rectangle(SKETCH_39_W, SKETCH_39_H)
    extrude(amount=-CUT_EXTRUDE_16_DEPTH, mode=Mode.SUBTRACT)

    # 草图40 → 切除-拉伸17 (cut)
    with BuildSketch(Plane.XY.offset(126)):
        with Locations((0, -650)):
            Rectangle(SKETCH_40_W, SKETCH_40_H)
    extrude(amount=-CUT_EXTRUDE_17_DEPTH, mode=Mode.SUBTRACT)

    # 草图43 → 切除-拉伸20 (cut)
    with BuildSketch(Plane(origin=(0, -300, 0), x_dir=(1, 0, 0), z_dir=(0, 1, 0))):
        with Locations(Location((800, 3524, 0), (0, 0, 270))):
            Circle(SKETCH_43_R)
        with Locations(Location((-800, 3524, 0), (0, 0, 270))):
            Circle(SKETCH_43_R)
        with Locations(Location((815, 1724, 0), (0, 0, 270))):
            Circle(SKETCH_43_R)
        with Locations(Location((-815, 1724, 0), (0, 0, 270))):
            Circle(SKETCH_43_R)
        with Locations(Location((800, -76, 0), (0, 0, 180))):
            Circle(SKETCH_43_R)
        with Locations((-800, -76)):
            Circle(SKETCH_43_R)
    extrude(amount=-CUT_EXTRUDE_20_DEPTH, mode=Mode.SUBTRACT)

    # 草图44 → 凸台-拉伸24 (add)
    with BuildSketch(Plane(origin=(0, -300, 0), x_dir=(1, 0, 0), z_dir=(0, 1, 0))):
        Polygon((-500, -126), (-500, -826), (500, -826), (1000, -826), (1000, -126), (500, -126), align=None)
    extrude(amount=-EXTRUDE_24_DEPTH)

    # 草图45 → 凸台-拉伸25 (add, symmetric)
    with BuildSketch(Plane(origin=(0, 0, 0), x_dir=(0, 0, -1), z_dir=(1, 0, 0))):
        Polygon((-726, -350), (-126, -650), (-126, -350), align=None)
    extrude_25 = extrude(amount=EXTRUDE_25_DEPTH, both=True)

    # 阵列(线性)1: 凸台-拉伸25 ×4
    with Locations(*[(-i * PATTERN_LINEAR_1_PITCH, 0, 0) for i in range(1, PATTERN_LINEAR_1_COUNT)]):
        add(extrude_25)

    # 阵列(线性)2: 凸台-拉伸25 ×8
    with Locations(*[(i * PATTERN_LINEAR_2_PITCH, 0, 0) for i in range(1, PATTERN_LINEAR_2_COUNT)]):
        add(extrude_25)

    # 草图46 → 凸台-拉伸26 (add)
    with BuildSketch(Plane(origin=(0, -300, 0), x_dir=(1, 0, 0), z_dir=(0, 1, 0))):
        with Locations((0, -537.5)):
            Rectangle(SKETCH_46_W, SKETCH_46_H)
    extrude(amount=EXTRUDE_26_DEPTH)

    # 草图47 → 凸台-拉伸28 (add)
    with BuildSketch(Plane(origin=(0, -300, 0), x_dir=(1, 0, 0), z_dir=(0, 1, 0))):
        with Locations((780, -540)):
            Rectangle(SKETCH_47_W, SKETCH_47_H)
    extrude(amount=EXTRUDE_28_DEPTH)


solid = part_1.part
